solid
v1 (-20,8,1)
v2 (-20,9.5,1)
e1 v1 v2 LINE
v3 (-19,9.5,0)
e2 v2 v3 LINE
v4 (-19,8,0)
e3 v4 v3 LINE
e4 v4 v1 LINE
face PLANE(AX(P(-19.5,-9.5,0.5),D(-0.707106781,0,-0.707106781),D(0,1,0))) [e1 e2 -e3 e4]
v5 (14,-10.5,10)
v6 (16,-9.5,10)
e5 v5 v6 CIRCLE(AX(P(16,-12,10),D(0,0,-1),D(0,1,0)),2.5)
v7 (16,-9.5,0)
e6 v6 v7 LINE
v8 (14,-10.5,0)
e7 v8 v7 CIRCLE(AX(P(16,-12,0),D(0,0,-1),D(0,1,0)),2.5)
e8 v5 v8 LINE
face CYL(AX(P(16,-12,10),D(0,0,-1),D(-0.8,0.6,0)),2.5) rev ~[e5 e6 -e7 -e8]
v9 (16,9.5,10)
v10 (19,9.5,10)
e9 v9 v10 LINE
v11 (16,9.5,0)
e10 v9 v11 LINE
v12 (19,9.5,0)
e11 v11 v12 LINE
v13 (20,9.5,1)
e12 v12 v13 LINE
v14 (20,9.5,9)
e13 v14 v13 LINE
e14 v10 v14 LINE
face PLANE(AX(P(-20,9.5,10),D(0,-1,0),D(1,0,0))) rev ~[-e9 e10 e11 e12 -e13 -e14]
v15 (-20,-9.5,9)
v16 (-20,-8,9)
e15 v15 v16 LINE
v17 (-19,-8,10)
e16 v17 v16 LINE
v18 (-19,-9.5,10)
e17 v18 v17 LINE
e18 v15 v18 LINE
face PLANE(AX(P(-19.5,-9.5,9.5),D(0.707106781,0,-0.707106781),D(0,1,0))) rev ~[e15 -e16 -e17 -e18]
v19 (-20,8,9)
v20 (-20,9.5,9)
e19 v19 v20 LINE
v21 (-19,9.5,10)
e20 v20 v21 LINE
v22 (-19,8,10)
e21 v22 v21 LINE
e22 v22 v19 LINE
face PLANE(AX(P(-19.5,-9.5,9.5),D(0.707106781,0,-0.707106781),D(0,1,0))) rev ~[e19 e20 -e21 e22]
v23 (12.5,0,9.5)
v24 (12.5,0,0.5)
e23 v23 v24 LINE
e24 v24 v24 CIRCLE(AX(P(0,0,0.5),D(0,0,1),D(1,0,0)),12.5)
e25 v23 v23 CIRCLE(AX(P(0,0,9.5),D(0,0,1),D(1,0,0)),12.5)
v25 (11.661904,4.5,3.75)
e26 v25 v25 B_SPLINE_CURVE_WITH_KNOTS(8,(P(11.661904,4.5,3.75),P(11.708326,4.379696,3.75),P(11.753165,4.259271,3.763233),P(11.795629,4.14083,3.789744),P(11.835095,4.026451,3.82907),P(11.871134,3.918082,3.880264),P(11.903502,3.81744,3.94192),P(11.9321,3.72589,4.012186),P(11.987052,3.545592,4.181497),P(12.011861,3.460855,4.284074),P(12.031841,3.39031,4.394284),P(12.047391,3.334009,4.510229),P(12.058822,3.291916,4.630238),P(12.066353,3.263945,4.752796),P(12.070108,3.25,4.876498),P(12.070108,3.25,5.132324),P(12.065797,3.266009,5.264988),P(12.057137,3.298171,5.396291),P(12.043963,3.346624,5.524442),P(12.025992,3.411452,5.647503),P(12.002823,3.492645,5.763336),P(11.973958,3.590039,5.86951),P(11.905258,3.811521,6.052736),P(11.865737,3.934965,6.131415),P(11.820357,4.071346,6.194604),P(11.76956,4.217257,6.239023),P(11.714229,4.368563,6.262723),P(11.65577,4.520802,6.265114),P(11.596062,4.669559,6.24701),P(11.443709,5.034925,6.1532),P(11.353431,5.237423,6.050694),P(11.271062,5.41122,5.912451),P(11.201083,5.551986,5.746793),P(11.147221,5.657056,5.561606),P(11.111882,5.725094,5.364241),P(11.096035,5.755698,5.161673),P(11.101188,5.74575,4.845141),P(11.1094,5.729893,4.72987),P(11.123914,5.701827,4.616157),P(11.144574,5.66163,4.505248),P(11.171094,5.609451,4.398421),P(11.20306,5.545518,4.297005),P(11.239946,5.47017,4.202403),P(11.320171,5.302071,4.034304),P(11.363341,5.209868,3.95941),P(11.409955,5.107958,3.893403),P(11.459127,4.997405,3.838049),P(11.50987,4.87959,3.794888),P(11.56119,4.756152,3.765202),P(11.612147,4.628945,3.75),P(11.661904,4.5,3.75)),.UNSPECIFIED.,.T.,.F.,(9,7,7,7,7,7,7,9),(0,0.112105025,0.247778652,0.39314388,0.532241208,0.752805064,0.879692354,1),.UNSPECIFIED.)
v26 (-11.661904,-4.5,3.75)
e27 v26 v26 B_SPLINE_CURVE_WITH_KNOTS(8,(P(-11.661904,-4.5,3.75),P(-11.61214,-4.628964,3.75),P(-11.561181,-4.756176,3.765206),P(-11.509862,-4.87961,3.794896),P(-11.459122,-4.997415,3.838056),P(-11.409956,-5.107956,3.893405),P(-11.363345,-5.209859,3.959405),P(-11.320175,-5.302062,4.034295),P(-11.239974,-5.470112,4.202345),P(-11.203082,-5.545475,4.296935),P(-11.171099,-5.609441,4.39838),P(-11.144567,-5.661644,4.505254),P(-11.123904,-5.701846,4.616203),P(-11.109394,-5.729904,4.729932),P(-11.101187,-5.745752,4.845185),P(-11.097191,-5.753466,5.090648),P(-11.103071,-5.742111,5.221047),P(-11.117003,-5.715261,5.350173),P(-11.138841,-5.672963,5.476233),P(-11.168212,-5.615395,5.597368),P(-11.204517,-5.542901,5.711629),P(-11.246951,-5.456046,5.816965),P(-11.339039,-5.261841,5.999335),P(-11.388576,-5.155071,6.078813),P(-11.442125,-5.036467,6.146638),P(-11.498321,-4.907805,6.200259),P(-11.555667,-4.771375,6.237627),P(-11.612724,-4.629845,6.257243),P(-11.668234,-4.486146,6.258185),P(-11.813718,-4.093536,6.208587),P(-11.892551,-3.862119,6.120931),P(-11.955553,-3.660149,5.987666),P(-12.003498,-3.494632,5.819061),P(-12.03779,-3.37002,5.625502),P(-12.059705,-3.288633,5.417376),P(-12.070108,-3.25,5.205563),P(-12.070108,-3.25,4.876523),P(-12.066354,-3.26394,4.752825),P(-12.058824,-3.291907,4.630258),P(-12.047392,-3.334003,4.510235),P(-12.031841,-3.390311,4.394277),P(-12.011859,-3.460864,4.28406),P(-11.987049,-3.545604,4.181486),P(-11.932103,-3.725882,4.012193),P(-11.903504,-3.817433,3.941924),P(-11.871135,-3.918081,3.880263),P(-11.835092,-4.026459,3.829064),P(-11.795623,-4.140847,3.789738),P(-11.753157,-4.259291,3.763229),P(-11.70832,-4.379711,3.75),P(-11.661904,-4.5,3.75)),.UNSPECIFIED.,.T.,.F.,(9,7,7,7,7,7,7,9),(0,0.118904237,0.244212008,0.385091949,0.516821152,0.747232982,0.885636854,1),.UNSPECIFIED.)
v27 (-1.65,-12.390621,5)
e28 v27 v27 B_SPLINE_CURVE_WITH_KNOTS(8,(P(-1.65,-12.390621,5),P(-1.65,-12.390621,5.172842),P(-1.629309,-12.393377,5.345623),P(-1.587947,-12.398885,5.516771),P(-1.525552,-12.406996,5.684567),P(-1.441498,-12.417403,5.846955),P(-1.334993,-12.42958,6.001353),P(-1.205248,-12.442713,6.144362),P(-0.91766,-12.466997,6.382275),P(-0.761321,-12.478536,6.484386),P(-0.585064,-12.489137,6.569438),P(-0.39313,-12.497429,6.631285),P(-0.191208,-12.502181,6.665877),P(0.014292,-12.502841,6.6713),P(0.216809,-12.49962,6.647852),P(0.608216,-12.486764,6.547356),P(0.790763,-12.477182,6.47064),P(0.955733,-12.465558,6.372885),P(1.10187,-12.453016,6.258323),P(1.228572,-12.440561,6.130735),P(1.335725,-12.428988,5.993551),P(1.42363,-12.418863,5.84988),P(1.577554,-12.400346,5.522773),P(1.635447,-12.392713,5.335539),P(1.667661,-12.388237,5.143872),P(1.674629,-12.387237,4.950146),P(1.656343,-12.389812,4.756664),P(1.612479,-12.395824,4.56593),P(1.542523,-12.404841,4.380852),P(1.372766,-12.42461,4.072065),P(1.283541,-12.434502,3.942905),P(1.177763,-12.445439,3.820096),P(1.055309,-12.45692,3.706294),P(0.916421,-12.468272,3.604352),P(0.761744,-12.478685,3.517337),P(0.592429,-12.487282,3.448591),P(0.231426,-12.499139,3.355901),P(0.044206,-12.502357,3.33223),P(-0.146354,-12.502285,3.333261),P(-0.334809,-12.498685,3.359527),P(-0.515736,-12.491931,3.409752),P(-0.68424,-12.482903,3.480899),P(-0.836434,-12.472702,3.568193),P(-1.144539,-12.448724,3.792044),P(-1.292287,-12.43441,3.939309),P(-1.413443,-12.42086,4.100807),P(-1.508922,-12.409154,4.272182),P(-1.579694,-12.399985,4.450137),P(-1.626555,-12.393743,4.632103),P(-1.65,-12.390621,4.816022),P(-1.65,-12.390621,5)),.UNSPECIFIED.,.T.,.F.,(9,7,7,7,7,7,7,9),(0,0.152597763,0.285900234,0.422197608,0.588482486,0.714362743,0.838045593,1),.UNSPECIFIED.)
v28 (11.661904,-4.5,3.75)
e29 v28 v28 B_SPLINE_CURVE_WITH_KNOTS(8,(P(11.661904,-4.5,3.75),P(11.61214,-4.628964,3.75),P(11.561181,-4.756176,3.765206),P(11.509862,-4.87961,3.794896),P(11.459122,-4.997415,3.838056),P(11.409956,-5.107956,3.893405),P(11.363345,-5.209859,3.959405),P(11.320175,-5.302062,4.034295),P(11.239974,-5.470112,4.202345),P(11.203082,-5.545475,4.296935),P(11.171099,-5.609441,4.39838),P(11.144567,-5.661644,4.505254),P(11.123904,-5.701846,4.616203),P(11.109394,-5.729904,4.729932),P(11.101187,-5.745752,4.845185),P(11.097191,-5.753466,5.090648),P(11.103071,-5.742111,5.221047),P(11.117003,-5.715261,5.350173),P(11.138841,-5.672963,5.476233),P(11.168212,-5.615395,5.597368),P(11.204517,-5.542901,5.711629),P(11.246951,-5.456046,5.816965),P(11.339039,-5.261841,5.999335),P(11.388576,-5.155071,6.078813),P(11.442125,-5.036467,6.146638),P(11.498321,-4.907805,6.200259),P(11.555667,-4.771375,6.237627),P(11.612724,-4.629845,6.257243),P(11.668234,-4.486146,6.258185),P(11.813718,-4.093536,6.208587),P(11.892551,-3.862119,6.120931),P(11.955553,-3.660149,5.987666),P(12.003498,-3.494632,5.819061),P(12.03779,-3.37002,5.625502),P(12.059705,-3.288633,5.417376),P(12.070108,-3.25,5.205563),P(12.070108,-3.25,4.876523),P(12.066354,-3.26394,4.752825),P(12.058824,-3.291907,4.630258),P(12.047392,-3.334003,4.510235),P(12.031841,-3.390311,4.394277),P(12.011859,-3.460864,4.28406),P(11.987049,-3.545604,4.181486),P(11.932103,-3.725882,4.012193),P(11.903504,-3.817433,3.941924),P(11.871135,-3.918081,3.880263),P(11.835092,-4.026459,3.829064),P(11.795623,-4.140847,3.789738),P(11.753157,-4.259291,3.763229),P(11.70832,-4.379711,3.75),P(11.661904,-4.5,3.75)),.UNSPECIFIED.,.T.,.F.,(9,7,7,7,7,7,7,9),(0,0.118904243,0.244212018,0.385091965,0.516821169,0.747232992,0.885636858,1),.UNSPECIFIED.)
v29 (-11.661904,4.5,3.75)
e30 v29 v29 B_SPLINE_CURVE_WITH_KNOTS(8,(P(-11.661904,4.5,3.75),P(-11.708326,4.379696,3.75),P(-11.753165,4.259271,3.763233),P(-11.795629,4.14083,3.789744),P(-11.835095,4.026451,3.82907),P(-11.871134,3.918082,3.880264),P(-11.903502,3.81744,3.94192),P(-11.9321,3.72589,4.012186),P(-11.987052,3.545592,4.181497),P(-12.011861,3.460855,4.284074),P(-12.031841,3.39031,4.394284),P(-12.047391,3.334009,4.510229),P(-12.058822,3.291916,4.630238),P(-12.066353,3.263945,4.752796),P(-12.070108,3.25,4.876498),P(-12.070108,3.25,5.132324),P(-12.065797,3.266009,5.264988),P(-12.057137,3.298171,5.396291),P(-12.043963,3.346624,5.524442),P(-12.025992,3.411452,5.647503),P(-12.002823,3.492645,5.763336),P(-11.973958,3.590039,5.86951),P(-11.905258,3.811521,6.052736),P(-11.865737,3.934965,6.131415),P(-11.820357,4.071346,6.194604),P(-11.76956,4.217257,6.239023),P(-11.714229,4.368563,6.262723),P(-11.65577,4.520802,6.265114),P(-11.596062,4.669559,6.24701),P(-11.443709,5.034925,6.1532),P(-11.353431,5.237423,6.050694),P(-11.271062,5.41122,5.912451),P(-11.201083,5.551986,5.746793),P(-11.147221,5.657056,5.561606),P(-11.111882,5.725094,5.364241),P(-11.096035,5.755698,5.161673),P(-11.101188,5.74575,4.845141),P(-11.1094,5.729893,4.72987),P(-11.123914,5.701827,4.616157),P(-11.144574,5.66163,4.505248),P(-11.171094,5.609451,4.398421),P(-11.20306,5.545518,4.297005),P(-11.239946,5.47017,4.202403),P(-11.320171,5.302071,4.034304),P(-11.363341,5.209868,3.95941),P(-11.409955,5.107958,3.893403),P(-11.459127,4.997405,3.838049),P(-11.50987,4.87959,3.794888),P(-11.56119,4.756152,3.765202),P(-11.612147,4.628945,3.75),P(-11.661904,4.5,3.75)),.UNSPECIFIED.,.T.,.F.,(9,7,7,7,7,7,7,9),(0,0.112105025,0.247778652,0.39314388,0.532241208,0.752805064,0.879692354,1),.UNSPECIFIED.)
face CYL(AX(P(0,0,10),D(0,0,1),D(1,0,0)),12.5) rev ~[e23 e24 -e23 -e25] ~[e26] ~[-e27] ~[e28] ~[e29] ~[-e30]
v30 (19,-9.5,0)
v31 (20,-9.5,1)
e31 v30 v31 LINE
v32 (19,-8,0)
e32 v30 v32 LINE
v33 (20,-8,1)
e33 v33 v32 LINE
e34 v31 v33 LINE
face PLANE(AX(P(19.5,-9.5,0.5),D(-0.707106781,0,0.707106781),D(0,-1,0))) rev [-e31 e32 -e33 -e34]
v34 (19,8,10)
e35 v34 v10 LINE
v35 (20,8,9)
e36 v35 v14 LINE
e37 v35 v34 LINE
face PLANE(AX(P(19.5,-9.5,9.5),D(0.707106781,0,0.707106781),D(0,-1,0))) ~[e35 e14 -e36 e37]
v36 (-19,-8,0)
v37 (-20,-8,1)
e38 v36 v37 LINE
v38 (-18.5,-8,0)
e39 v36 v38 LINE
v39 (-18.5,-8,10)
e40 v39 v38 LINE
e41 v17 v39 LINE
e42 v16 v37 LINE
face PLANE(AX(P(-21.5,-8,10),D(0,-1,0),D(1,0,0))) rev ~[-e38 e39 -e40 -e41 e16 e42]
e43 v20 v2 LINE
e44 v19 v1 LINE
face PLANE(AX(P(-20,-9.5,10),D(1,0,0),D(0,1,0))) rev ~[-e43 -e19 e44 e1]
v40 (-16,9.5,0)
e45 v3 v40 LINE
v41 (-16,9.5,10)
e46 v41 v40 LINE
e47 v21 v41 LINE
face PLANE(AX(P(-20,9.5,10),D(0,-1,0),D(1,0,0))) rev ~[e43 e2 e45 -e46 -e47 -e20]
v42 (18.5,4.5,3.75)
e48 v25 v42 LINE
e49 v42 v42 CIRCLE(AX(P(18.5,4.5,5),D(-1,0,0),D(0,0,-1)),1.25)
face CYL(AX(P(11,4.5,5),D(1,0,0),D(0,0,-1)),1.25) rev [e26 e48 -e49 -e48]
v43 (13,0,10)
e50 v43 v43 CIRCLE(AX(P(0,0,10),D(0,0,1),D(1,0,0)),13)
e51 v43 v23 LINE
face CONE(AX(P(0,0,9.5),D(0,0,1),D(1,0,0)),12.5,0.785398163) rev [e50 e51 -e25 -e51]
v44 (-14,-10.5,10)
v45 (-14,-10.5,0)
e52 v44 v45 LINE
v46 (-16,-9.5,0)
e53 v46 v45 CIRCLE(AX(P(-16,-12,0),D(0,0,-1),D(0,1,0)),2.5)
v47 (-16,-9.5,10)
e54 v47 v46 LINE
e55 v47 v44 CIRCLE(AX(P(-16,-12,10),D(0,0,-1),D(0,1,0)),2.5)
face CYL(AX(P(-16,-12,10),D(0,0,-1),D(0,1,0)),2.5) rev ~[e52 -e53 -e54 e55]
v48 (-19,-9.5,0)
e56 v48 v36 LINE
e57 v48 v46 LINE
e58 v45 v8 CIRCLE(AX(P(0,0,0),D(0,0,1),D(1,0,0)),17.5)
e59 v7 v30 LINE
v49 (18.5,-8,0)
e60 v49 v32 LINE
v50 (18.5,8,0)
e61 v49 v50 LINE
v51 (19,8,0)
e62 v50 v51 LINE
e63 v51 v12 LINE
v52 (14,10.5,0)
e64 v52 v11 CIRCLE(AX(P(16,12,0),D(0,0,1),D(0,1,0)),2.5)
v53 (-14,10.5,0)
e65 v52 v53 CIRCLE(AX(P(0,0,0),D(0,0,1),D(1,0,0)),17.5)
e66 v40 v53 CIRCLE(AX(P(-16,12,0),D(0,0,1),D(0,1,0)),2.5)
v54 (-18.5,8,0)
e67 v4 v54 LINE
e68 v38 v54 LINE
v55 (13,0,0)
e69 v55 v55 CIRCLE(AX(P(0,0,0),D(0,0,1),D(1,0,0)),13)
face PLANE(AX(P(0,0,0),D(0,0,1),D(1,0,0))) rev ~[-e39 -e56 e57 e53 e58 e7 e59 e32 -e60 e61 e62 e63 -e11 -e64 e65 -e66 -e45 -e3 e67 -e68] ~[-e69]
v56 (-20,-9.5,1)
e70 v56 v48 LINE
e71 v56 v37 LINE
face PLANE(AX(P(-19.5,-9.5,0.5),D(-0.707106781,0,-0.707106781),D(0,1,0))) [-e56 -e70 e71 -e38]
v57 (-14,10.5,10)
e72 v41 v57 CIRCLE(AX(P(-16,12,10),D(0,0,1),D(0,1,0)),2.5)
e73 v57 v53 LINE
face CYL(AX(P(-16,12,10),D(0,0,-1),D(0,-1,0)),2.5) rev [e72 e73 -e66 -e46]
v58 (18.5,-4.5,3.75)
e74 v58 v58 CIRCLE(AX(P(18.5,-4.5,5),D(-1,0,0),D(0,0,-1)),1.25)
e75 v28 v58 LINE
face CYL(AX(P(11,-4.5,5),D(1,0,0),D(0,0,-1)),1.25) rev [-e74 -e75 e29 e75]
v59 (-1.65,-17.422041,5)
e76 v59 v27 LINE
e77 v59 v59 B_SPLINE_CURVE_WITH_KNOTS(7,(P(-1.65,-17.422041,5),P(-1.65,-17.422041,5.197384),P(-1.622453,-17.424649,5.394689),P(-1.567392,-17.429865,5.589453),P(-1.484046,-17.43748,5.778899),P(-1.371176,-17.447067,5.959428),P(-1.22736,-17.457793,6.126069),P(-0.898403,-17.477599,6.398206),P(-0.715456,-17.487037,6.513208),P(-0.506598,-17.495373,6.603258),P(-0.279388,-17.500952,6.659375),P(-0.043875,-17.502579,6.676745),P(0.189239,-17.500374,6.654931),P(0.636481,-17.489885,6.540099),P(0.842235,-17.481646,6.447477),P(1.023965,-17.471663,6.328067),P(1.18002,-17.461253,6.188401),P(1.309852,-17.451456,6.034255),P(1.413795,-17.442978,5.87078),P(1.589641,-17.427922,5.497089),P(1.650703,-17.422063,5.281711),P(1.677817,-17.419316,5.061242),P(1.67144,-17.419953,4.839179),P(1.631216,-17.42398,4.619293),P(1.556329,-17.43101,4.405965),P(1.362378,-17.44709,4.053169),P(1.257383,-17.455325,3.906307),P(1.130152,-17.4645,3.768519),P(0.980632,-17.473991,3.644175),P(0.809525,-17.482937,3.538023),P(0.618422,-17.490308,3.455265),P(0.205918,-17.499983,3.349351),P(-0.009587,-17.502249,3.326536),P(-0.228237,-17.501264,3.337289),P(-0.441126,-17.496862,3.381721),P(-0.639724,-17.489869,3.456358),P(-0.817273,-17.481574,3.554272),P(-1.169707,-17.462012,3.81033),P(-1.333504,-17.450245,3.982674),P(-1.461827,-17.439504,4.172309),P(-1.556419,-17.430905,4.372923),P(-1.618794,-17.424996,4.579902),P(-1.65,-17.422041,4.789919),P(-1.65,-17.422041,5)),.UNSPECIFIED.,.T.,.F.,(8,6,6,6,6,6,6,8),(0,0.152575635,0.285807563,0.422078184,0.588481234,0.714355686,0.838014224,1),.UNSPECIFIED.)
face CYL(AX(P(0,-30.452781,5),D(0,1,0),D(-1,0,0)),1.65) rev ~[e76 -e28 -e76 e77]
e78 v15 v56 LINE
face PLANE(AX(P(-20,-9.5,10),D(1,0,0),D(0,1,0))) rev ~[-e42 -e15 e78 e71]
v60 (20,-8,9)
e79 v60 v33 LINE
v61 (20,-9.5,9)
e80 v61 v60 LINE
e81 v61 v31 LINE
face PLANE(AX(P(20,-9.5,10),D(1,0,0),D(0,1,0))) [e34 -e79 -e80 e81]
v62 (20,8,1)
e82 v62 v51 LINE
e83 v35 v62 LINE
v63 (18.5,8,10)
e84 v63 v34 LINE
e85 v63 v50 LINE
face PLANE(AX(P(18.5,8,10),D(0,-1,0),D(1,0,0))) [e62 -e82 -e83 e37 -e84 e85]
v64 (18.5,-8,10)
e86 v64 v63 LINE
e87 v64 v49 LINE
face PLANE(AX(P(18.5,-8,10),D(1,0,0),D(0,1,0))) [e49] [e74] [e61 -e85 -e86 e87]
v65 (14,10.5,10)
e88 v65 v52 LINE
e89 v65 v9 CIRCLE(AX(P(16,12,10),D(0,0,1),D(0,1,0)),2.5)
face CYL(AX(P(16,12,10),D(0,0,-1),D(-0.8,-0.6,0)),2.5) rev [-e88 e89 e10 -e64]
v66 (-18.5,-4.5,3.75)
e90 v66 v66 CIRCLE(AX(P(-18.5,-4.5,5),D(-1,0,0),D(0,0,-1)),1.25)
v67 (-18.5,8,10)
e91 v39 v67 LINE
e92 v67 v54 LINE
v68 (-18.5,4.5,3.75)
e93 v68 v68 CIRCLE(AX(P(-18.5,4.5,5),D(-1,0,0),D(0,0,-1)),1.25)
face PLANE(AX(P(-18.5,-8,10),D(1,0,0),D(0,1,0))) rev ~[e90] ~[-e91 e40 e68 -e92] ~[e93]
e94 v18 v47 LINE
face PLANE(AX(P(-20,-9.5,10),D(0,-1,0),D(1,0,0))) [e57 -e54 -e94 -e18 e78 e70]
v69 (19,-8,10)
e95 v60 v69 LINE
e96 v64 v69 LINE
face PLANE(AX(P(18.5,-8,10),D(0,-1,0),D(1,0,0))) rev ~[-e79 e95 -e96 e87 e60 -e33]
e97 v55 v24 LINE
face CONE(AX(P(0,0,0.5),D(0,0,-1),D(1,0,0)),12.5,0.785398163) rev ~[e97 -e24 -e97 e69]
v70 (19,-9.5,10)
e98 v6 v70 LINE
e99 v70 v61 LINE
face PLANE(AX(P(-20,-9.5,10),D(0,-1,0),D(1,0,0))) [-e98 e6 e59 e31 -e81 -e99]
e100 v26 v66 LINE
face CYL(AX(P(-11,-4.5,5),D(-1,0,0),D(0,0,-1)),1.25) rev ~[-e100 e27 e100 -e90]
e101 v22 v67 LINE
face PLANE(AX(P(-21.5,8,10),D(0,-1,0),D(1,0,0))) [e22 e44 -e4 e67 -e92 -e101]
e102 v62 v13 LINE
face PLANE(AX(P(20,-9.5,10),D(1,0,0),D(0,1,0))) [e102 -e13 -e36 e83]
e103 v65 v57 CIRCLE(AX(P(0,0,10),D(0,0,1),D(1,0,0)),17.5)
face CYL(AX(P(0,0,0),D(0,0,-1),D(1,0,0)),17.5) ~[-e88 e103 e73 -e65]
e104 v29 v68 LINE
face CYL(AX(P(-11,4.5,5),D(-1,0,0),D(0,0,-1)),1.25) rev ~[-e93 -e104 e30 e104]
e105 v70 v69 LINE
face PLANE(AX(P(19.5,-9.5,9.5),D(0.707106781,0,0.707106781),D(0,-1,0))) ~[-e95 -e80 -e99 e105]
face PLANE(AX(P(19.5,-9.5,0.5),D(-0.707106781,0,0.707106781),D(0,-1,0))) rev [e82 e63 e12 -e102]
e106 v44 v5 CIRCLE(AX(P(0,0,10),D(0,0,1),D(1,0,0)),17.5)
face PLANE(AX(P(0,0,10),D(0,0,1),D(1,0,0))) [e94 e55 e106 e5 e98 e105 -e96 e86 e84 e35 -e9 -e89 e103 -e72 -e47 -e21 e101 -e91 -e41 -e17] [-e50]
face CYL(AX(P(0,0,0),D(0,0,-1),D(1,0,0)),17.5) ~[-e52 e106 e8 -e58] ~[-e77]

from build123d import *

# Parameters (mm, degrees)
SKETCH1_R                  = 17.5
BOSS_EXTRUDE1_DEPTH        = 10
SKETCH2_W                  = 40
SKETCH2_H                  = 19
BOSS_EXTRUDE2_DEPTH        = 10
CHAMFER1_SIZE              = 1
SKETCH3_R                  = 12.5
CUT_EXTRUDE1_DEPTH         = 29.394541729
SKETCH4_W                  = 3
SKETCH4_H                  = 16
CUT_EXTRUDE2_DEPTH         = 29.394541729
M4_TAPPED_HOLE1_D          = 3.3
M4_TAPPED_HOLE1_DEPTH      = 10.1
M4_TAPPED_HOLE1_TIP        = 0.991420021
FILLET1_R                  = 2.5
M3_TAPPED_HOLE1_AT_2_COUNT = 2
M3_TAPPED_HOLE1_AT_2_PITCH = 9
CHAMFER2_SIZE              = 0.5


with BuildPart() as part:
    # Sketch1 → Boss-Extrude1 (new body)
    with BuildSketch(Plane.XY):
        Circle(SKETCH1_R)
    extrude(amount=BOSS_EXTRUDE1_DEPTH)

    # Sketch2 → Boss-Extrude2 (add)
    with BuildSketch(Plane.XY.offset(10)):
        Rectangle(SKETCH2_W, SKETCH2_H)
    extrude(amount=-BOSS_EXTRUDE2_DEPTH)

    # Chamfer1
    chamfer1_edges = [part.edges().sort_by_distance(p)[0] for p in [
        (20, 0, 10),
        (-20, 0, 10),
        (-20, 0, 0),
        (20, 0, 0),
    ]]
    chamfer(chamfer1_edges, length=CHAMFER1_SIZE)

    # Sketch3 → Cut-Extrude1 (cut, through all)
    with BuildSketch(Plane.XY.offset(10)):
        Circle(SKETCH3_R)
    extrude(amount=-CUT_EXTRUDE1_DEPTH, mode=Mode.SUBTRACT)

    # Sketch4 → Cut-Extrude2 (cut, through all)
    with BuildSketch(Plane.XY.offset(10)):
        with Locations((20, 0)):
            Rectangle(SKETCH4_W, SKETCH4_H)
        with Locations((-20, 0)):
            Rectangle(SKETCH4_W, SKETCH4_H)
    extrude(amount=-CUT_EXTRUDE2_DEPTH, mode=Mode.SUBTRACT)

    # M4 Tapped Hole1
    with Locations(Plane.XZ.offset(20.35278131)):
        with Locations((0, 5)):
            Hole(M4_TAPPED_HOLE1_D / 2, depth=M4_TAPPED_HOLE1_DEPTH)
            with Locations((0, 0, -(M4_TAPPED_HOLE1_DEPTH + M4_TAPPED_HOLE1_TIP / 2))):  # 118° drill point
                Cone(0, M4_TAPPED_HOLE1_D / 2, M4_TAPPED_HOLE1_TIP, mode=Mode.SUBTRACT)

    # Fillet1
    fillet1_edges = [part.edges().sort_by_distance(p)[0] for p in [
        (-14.696938457, -9.5, 5),
        (14.696938457, -9.5, 5),
        (14.696938457, 9.5, 5),
        (-14.696938457, 9.5, 5),
    ]]
    fillet(fillet1_edges, radius=FILLET1_R)

    # Sketch7 → M3 Tapped Hole1 (revolve, cut)
    with BuildSketch(Plane(origin=(18.5, -4.5, 5), x_dir=(0, 0, -1), z_dir=(0, 1, 0))):
        Polygon((0, 0), (0, 8.251075774), (1.25, 7.5), (1.25, 0), align=None)
    m3_tapped_hole1 = revolve(axis=Axis((24.85, -4.5, 5), (-1, 0, 0)), mode=Mode.SUBTRACT)

    # M3 Tapped Hole1 at 2: M3 Tapped Hole1 ×2
    with Locations(*[(0, i * M3_TAPPED_HOLE1_AT_2_PITCH, 0) for i in range(1, M3_TAPPED_HOLE1_AT_2_COUNT)]):
        add(m3_tapped_hole1, mode=Mode.SUBTRACT)

    # Mirror1: M3 Tapped Hole1 across plane
    add(m3_tapped_hole1.mirror(Plane(origin=(0, 0, 0), x_dir=(0, 0, 1), z_dir=(1, 0, 0))), mode=Mode.SUBTRACT)

    # Mirror1 copy 1 sketch → Mirror1 copy 1 (revolve, cut)
    with BuildSketch(Plane(origin=(-18.5, 4.5, 5), x_dir=(0, 0, -1), z_dir=(0, 1, 0))):
        Polygon((0, 0), (0, -8.251075774), (1.25, -7.5), (1.25, 0), align=None)
    revolve(axis=Axis((-24.85, 4.5, 5), (-1, 0, 0)), mode=Mode.SUBTRACT)

    # Chamfer2
    chamfer2_edges = [part.edges().sort_by_distance(p)[0] for p in [
        (-12.5, 0, 0),
        (-12.5, 0, 10),
    ]]
    chamfer(chamfer2_edges, length=CHAMFER2_SIZE)


solid = part.part
